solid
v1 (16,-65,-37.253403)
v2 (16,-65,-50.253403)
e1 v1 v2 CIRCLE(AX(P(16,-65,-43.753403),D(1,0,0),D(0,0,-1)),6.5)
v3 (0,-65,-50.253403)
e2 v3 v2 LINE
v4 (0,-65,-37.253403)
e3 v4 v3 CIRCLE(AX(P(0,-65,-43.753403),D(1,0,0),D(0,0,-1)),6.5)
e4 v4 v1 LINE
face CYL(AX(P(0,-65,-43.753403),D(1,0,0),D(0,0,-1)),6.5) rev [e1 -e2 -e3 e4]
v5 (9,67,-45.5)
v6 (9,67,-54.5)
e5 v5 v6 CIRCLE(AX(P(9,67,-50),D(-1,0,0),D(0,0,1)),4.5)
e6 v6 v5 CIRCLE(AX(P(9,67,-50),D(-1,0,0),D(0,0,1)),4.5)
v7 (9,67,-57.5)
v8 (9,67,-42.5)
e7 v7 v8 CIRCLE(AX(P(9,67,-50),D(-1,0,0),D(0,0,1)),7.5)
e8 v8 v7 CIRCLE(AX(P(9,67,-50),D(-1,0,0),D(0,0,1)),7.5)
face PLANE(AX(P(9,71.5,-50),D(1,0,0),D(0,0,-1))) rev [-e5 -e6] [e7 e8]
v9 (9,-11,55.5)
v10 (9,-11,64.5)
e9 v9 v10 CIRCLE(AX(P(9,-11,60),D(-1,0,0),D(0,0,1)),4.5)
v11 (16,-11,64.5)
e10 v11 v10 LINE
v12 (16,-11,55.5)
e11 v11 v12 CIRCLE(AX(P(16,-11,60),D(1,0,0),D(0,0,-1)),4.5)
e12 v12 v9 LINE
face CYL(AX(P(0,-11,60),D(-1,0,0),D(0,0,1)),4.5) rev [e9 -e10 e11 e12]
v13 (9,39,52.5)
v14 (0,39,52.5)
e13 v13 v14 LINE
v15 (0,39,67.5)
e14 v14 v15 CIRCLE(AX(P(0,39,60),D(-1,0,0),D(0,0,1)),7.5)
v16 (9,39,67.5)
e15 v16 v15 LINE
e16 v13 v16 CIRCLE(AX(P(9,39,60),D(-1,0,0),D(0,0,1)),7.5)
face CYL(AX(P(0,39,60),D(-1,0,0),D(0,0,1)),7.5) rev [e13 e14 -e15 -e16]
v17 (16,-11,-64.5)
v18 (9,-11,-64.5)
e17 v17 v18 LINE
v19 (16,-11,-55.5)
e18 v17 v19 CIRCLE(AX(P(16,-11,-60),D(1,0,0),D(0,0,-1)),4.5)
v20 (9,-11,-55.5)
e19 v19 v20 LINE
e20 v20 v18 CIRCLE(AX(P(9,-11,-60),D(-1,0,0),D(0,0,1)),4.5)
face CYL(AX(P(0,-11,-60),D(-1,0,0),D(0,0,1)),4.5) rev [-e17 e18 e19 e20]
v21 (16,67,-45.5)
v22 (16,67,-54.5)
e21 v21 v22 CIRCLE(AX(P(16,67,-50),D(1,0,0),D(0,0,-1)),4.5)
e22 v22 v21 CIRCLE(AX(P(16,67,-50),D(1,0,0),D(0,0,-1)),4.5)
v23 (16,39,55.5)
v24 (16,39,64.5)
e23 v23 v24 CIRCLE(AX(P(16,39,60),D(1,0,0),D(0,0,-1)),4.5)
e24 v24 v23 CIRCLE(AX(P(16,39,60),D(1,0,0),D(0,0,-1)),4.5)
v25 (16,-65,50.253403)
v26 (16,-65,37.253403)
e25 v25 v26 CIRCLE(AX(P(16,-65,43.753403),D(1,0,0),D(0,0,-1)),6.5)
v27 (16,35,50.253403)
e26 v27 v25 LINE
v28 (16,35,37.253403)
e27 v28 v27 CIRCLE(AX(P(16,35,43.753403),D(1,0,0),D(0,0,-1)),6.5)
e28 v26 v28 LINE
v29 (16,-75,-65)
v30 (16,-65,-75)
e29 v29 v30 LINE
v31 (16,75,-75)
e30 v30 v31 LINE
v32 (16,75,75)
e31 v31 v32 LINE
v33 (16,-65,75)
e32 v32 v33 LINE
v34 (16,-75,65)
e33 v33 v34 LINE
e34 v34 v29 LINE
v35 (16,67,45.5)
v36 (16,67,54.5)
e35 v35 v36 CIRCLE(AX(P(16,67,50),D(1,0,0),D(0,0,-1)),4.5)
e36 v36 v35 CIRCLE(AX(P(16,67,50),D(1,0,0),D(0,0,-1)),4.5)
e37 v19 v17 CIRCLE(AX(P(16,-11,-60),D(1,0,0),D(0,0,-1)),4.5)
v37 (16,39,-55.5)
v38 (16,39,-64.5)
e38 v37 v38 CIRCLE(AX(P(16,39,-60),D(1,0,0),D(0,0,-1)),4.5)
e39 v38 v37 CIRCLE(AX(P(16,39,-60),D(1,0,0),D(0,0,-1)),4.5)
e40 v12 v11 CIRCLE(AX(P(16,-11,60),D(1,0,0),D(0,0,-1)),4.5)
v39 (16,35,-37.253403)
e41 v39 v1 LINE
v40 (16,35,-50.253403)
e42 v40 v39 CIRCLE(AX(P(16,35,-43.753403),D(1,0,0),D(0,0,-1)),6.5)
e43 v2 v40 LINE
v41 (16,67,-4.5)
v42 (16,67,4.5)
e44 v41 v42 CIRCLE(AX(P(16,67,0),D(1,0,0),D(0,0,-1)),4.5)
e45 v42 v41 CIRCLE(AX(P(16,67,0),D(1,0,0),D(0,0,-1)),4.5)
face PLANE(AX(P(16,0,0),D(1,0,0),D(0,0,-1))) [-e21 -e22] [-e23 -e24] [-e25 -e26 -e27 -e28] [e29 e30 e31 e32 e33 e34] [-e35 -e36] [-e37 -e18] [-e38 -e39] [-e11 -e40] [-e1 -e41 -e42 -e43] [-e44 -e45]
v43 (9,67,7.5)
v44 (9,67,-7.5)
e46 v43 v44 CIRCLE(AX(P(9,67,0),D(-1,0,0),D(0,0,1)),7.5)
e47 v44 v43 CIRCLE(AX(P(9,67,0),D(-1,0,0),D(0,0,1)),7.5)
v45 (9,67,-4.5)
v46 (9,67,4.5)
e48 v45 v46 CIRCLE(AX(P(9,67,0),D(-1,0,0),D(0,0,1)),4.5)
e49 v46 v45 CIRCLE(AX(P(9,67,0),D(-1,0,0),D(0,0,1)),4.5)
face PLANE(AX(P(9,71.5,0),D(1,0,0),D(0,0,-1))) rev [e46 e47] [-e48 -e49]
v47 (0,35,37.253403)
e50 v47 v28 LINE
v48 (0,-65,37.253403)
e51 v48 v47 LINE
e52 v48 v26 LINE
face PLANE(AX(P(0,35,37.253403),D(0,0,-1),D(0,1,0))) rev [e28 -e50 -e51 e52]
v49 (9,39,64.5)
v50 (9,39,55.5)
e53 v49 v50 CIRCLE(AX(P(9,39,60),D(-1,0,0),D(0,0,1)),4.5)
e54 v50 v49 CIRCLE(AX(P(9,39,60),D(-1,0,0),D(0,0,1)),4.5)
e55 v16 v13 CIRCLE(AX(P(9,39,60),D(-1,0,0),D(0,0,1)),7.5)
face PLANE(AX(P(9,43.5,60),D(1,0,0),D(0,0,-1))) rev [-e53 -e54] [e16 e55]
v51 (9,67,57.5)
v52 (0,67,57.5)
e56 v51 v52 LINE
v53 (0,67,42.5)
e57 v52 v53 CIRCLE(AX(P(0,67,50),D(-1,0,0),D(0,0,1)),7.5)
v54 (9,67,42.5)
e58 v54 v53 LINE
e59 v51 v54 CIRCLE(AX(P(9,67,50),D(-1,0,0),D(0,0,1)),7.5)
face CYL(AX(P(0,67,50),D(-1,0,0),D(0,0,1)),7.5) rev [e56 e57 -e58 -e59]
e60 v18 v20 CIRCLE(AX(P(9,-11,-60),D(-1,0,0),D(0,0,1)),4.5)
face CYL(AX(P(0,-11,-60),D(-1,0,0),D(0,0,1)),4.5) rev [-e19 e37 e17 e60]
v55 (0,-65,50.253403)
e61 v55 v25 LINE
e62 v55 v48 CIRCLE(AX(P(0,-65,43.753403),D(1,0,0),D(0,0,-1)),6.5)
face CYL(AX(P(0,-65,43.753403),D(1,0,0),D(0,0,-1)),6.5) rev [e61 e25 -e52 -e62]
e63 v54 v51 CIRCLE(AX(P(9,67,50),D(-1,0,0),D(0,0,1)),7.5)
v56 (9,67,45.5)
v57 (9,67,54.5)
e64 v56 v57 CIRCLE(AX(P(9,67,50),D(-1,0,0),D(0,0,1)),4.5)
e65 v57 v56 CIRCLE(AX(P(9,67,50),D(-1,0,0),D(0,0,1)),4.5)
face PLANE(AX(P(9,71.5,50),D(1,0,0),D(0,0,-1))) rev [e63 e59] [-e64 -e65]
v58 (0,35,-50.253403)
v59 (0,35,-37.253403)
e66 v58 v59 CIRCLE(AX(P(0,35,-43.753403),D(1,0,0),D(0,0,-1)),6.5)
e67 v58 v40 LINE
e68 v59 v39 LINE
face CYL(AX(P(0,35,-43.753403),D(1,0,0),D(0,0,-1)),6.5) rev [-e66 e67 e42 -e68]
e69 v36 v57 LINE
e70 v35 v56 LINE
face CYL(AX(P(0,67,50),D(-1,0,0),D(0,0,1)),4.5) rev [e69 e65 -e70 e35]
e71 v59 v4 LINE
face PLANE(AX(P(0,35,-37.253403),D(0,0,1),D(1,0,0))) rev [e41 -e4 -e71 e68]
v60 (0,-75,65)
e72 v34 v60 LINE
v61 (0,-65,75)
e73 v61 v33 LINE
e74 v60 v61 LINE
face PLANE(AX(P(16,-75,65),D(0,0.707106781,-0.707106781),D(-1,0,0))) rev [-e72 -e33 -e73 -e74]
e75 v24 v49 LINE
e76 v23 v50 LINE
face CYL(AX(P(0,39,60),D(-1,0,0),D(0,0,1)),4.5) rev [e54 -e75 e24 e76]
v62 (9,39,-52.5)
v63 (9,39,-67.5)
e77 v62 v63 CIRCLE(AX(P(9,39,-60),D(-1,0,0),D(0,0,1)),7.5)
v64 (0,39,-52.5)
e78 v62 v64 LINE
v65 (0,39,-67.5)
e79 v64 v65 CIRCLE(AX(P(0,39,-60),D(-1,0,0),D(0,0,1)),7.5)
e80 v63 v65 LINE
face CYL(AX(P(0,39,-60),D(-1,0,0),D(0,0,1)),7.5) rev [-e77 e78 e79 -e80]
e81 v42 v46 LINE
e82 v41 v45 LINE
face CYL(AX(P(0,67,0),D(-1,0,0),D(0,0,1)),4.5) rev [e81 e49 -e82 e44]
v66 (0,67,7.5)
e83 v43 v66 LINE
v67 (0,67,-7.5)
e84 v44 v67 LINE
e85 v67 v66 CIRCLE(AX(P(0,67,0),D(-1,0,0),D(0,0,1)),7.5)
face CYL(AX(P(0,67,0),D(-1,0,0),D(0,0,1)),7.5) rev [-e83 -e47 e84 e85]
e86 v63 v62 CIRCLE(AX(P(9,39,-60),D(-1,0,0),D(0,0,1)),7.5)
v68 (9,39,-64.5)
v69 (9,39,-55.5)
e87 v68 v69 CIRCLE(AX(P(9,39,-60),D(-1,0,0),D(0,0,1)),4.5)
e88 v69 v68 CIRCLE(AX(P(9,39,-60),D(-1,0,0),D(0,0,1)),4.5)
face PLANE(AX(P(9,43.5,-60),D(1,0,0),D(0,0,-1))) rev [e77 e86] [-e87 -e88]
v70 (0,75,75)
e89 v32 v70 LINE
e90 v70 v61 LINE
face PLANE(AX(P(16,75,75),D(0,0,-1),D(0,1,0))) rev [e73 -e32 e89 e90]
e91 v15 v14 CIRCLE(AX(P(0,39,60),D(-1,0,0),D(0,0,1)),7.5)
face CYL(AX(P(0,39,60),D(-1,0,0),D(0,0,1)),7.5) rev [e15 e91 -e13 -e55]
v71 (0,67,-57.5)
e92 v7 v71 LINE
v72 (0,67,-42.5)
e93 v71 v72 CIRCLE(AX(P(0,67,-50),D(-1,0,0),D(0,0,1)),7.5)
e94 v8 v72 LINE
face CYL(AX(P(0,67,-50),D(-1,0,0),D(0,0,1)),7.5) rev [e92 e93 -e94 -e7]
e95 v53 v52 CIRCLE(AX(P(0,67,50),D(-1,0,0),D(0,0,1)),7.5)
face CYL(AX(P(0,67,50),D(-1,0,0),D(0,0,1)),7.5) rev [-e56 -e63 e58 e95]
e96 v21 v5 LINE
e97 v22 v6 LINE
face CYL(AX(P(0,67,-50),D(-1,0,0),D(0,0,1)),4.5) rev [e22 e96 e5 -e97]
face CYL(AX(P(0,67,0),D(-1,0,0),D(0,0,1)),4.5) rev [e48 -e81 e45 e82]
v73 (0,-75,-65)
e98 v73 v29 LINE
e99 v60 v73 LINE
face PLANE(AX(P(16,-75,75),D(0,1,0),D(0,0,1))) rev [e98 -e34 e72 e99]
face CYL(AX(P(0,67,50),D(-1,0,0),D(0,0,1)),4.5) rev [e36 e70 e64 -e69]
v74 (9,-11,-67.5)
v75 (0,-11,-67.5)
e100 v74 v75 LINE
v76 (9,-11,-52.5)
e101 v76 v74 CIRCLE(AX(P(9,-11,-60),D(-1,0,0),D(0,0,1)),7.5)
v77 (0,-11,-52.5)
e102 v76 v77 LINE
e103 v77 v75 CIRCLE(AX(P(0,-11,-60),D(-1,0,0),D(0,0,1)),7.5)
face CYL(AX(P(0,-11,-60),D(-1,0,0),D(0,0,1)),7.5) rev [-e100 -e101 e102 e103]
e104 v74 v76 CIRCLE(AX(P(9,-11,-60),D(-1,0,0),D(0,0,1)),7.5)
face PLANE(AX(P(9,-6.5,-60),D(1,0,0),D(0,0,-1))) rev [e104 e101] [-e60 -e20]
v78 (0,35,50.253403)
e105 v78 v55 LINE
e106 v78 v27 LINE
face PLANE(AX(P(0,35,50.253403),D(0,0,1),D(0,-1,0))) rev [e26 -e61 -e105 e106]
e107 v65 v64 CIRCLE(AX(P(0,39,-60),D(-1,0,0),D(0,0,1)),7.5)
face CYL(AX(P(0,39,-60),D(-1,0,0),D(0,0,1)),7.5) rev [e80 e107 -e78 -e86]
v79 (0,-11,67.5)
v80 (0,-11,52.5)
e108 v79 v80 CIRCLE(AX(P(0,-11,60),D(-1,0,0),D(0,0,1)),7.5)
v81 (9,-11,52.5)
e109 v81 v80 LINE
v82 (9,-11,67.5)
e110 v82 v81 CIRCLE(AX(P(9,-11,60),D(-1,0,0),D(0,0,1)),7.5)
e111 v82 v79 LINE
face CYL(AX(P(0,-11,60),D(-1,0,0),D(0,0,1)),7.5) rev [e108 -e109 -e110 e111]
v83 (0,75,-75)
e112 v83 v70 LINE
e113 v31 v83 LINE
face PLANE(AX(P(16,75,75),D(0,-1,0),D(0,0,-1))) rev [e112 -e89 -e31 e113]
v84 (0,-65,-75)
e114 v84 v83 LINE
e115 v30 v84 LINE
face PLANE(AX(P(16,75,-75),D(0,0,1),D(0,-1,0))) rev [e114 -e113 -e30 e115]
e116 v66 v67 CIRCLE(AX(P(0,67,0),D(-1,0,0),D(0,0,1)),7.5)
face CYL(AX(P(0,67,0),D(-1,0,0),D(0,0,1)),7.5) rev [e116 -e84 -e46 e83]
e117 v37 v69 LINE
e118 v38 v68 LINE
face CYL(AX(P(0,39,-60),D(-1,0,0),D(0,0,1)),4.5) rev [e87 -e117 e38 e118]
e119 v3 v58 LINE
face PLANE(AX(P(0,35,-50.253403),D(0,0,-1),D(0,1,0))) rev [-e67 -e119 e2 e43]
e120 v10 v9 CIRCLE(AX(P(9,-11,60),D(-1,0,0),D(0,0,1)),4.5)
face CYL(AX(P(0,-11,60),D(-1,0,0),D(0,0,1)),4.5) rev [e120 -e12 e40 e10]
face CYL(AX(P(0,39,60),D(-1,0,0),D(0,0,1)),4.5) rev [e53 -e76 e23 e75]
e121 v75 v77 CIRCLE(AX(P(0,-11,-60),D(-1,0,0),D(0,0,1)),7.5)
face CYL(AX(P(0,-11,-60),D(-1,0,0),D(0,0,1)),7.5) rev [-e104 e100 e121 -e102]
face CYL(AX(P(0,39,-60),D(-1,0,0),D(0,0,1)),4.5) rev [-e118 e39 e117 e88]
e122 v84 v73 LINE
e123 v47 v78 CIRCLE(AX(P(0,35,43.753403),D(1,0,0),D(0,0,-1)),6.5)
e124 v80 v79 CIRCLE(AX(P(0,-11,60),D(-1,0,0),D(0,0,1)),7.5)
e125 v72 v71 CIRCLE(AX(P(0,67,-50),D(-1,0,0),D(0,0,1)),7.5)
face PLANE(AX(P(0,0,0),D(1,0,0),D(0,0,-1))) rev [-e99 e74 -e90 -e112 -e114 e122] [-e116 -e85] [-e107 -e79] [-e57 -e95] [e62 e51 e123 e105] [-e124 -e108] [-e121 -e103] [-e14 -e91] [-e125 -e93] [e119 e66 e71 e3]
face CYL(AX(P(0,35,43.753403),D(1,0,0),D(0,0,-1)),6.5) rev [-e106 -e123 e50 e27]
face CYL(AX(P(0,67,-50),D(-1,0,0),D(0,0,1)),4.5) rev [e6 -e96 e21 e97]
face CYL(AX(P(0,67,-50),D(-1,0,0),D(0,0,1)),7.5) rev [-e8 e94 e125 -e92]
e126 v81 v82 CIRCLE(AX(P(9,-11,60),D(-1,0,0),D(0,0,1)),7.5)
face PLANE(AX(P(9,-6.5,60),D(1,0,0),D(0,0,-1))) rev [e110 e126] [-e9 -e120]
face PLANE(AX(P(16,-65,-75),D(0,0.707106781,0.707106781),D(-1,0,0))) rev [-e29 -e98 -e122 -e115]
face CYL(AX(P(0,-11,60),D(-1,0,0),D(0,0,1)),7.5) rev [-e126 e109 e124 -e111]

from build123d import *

# Parameters (mm, degrees)
SKETCH_1_W                = 150
SKETCH_1_H                = 150
EXTRUDE_1_DEPTH           = 16
CUT_EXTRUDE_1_DEPTH       = 108.266024444
HOLE_WIZARD_1_D           = 9
HOLE_WIZARD_1_DEPTH       = 29.25
HOLE_WIZARD_1_CBORE_D     = 15
HOLE_WIZARD_1_CBORE_DEPTH = 9
HOLE_WIZARD_1_TIP         = 2.703872786
HOLE_WIZARD_2_D           = 9
HOLE_WIZARD_2_DEPTH       = 29.25
HOLE_WIZARD_2_CBORE_D     = 15
HOLE_WIZARD_2_CBORE_DEPTH = 9
HOLE_WIZARD_2_TIP         = 2.703872786
CHAMFER_1_SIZE            = 10


with BuildPart() as part:
    # 草图1 → 凸台-拉伸1 (new body)
    with BuildSketch(Plane(origin=(0, 0, 0), x_dir=(0, 0, -1), z_dir=(1, 0, 0))):
        Rectangle(SKETCH_1_W, SKETCH_1_H)
    extrude(amount=EXTRUDE_1_DEPTH)

    # 草图3 → 切除-拉伸1 (cut, through all)
    with BuildSketch(Plane(origin=(16, 0, 0), x_dir=(0, 0, -1), z_dir=(1, 0, 0))):
        with BuildLine():
            Line((-37.253402877, 35), (-37.253402877, -65))
            ThreePointArc((-37.253402877, -65), (-43.753402877, -71.5), (-50.253402877, -65))
            Line((-50.253402877, -65), (-50.253402877, 35))
            ThreePointArc((-50.253402877, 35), (-43.753402877, 41.5), (-37.253402877, 35))
        make_face()
        with BuildLine():
            Line((50.253402877, 35), (50.253402877, -65))
            ThreePointArc((50.253402877, -65), (43.753402877, -71.5), (37.253402877, -65))
            Line((37.253402877, -65), (37.253402877, 35))
            ThreePointArc((37.253402877, 35), (43.753402877, 41.5), (50.253402877, 35))
        make_face()
    extrude(amount=-CUT_EXTRUDE_1_DEPTH, mode=Mode.SUBTRACT)

    # 打孔尺寸(%根据)内六角圆柱头螺钉的类型1
    with Locations(Plane.ZY):
        with Locations((-50, 67), (0, 67), (50, 67)):
            CounterBoreHole(HOLE_WIZARD_1_D / 2, HOLE_WIZARD_1_CBORE_D / 2, HOLE_WIZARD_1_CBORE_DEPTH, depth=HOLE_WIZARD_1_DEPTH)
            with Locations((0, 0, -(HOLE_WIZARD_1_DEPTH + HOLE_WIZARD_1_TIP / 2))):  # 118° drill point
                Cone(0, HOLE_WIZARD_1_D / 2, HOLE_WIZARD_1_TIP, mode=Mode.SUBTRACT)

    # 打孔尺寸(%根据)内六角圆柱头螺钉的类型2
    with Locations(Plane.ZY):
        with Locations((-60, 39), (-60, -11), (60, 39), (60, -11)):
            CounterBoreHole(HOLE_WIZARD_2_D / 2, HOLE_WIZARD_2_CBORE_D / 2, HOLE_WIZARD_2_CBORE_DEPTH, depth=HOLE_WIZARD_2_DEPTH)
            with Locations((0, 0, -(HOLE_WIZARD_2_DEPTH + HOLE_WIZARD_2_TIP / 2))):  # 118° drill point
                Cone(0, HOLE_WIZARD_2_D / 2, HOLE_WIZARD_2_TIP, mode=Mode.SUBTRACT)

    # 倒角1
    chamfer_1_edges = [part.edges().sort_by_distance(p)[0] for p in [
        (8, -75, -75),
        (8, -75, 75),
    ]]
    chamfer(chamfer_1_edges, length=CHAMFER_1_SIZE)


solid = part.part
